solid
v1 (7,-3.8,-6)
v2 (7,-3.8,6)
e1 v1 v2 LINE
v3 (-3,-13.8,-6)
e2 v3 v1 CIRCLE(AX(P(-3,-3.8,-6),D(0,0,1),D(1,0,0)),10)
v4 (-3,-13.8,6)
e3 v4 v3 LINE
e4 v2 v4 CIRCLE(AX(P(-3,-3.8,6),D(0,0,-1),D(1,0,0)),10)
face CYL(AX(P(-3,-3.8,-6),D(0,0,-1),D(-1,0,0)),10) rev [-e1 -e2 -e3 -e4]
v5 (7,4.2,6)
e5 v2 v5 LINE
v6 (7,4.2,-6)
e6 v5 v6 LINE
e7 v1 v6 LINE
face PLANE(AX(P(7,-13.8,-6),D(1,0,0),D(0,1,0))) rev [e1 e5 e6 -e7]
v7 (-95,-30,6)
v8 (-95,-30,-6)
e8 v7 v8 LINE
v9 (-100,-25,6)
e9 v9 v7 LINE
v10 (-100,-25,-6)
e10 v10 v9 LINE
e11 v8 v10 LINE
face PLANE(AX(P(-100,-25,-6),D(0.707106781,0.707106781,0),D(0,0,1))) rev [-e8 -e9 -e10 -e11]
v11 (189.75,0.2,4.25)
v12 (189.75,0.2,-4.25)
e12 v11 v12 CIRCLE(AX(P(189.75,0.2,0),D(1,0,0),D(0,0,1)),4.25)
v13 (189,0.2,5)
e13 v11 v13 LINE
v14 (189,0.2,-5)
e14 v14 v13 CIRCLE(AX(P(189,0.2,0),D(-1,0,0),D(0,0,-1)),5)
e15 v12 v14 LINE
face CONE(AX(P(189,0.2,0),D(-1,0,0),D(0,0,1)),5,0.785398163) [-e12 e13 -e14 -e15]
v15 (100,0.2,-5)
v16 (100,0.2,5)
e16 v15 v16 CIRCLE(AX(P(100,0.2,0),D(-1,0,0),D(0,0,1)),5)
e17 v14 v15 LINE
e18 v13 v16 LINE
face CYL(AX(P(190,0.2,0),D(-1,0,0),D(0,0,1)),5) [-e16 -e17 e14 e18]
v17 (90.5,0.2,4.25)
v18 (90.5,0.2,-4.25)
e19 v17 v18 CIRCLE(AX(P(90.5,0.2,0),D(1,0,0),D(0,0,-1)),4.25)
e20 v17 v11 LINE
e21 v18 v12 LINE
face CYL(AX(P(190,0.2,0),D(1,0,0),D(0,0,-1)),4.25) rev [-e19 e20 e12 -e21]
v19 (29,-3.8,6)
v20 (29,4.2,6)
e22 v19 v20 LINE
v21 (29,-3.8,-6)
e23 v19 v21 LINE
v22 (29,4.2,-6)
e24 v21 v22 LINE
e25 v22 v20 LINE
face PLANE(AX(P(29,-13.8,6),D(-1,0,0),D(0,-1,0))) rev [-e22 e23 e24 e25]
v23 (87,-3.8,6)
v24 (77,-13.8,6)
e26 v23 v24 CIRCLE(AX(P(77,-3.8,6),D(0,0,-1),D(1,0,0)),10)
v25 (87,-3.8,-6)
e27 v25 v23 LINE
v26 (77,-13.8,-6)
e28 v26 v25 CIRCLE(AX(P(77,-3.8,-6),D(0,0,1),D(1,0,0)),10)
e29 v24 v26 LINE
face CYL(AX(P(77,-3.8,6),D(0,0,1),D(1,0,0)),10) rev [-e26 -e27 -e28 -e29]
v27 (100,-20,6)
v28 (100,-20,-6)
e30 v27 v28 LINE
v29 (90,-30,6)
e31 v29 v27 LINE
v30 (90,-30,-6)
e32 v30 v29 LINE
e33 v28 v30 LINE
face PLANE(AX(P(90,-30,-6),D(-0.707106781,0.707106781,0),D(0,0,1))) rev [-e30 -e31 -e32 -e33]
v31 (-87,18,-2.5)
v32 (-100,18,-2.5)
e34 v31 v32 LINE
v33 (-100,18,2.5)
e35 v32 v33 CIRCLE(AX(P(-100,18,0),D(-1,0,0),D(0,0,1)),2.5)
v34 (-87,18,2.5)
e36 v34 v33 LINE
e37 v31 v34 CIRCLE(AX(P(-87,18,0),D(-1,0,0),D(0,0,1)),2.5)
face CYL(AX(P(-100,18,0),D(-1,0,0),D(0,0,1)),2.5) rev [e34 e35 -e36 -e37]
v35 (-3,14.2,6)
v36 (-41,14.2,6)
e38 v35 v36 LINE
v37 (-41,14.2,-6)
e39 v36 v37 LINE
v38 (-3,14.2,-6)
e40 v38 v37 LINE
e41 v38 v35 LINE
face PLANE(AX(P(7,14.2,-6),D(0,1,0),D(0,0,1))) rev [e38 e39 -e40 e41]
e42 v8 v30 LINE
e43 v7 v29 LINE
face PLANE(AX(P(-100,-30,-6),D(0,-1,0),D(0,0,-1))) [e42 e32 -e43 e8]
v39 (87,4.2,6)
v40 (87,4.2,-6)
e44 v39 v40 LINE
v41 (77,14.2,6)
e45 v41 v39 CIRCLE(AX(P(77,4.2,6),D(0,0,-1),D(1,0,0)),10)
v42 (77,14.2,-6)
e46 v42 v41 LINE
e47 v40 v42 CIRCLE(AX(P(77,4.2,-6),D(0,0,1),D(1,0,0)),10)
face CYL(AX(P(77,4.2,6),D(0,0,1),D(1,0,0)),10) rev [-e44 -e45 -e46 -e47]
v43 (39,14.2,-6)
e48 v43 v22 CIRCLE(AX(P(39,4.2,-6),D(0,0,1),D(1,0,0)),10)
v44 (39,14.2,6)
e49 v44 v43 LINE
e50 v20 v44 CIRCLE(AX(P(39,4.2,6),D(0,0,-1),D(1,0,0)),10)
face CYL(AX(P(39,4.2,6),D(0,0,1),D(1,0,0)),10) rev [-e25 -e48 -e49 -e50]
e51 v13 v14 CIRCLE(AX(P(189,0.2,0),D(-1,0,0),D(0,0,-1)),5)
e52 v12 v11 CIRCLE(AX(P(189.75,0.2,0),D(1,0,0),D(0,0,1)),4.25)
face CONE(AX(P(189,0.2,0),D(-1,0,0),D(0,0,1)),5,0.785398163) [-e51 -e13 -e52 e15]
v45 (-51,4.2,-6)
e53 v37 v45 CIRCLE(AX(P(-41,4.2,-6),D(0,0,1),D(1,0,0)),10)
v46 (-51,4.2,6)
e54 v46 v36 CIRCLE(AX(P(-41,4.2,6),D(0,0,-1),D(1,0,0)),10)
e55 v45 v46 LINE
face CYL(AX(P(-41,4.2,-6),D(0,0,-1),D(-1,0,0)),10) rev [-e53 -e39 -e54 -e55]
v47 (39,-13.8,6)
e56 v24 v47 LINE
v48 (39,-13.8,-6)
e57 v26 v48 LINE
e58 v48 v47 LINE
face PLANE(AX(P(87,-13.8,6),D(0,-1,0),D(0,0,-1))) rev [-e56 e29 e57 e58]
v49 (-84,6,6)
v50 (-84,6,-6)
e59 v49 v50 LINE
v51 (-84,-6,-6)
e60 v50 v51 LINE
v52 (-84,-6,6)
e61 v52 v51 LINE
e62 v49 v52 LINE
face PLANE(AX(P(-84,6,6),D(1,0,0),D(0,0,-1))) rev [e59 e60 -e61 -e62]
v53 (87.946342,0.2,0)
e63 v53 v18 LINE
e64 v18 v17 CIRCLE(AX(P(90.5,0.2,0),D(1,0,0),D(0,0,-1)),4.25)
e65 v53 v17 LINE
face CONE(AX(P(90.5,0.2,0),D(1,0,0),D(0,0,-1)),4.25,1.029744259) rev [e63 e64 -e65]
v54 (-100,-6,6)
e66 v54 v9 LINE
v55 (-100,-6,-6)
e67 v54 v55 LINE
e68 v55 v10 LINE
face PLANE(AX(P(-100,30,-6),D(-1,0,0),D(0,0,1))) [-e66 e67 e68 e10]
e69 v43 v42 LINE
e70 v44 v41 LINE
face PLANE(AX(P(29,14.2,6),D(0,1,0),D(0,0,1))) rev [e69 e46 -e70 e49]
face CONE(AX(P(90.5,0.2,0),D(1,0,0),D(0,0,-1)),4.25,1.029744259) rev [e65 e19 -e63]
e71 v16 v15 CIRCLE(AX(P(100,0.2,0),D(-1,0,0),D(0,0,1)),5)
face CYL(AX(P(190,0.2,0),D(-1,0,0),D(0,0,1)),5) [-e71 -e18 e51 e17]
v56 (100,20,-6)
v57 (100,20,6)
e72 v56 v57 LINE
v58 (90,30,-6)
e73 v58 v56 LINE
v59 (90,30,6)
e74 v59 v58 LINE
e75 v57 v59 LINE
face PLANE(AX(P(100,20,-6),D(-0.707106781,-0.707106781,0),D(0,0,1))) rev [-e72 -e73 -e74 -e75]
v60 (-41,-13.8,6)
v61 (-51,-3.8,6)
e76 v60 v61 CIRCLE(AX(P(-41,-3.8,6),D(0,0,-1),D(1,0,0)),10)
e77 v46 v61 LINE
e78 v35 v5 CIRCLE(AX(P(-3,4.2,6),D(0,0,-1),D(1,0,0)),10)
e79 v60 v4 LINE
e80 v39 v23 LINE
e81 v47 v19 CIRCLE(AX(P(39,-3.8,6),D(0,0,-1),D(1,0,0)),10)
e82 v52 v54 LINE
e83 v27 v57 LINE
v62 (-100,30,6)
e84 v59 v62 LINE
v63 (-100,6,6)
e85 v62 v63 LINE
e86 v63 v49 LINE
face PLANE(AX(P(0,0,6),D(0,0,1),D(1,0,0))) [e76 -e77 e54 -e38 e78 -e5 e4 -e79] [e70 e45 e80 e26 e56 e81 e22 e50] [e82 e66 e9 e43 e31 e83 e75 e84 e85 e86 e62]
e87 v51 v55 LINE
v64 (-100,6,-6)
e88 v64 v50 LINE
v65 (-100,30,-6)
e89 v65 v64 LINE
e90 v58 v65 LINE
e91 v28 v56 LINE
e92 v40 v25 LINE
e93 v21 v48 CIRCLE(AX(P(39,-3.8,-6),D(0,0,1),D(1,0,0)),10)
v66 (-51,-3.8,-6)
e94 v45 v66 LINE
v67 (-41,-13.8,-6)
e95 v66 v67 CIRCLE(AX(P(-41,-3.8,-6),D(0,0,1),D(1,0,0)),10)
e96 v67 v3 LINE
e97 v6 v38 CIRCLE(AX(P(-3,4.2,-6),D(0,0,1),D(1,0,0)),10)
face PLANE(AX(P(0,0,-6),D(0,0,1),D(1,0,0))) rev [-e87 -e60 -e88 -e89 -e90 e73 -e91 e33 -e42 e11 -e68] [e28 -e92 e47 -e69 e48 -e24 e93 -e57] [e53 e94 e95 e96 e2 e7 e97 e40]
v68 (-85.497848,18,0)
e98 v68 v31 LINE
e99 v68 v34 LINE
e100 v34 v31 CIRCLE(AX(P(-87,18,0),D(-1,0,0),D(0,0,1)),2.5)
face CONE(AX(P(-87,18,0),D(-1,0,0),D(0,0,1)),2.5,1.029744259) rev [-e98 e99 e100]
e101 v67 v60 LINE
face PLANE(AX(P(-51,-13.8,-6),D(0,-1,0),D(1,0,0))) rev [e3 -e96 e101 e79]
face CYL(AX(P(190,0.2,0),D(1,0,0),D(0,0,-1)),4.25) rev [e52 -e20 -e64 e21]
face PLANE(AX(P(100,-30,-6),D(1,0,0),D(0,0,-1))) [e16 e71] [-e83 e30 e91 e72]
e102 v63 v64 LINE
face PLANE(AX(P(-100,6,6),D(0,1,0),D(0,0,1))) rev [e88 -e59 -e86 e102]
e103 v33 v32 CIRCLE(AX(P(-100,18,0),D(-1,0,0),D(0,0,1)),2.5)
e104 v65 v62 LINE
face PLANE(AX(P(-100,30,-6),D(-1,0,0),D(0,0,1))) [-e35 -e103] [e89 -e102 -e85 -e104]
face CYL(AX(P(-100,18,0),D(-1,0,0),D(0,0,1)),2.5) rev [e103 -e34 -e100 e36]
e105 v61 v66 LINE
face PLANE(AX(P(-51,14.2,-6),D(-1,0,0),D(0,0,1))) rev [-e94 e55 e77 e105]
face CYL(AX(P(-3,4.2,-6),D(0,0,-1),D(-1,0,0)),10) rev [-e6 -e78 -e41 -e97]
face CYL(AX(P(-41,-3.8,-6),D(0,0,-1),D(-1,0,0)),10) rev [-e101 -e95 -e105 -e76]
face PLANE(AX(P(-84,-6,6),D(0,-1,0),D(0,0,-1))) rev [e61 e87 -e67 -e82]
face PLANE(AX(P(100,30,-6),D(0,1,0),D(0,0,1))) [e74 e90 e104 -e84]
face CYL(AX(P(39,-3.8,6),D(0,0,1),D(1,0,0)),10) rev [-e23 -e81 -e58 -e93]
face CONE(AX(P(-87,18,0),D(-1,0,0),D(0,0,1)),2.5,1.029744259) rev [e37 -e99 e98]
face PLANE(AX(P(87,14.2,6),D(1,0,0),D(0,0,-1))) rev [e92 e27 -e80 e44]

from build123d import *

# Parameters (mm, degrees)
SKETCH1_W              = 200
SKETCH1_H              = 60
BOSS_EXTRUDE1_DEPTH    = 12
SKETCH2_W              = 16
SKETCH2_H              = 12
CUT_EXTRUDE1_DEPTH     = 106.090437243
SKETCH3_W              = 58
SKETCH3_H              = 28
CUT_EXTRUDE2_DEPTH     = 106.090437243
SKETCH4_W              = 58
SKETCH4_H              = 28
CUT_EXTRUDE3_DEPTH     = 106.090437243
SKETCH5_W              = 90
SKETCH5_H              = 5
M6_TAPPED_HOLE1_D      = 5
M6_TAPPED_HOLE1_DEPTH  = 13
M6_TAPPED_HOLE1_TIP    = 1.502151548
CHAMFER1_SIZE          = 1
CHAMFER2_SIZE          = 10
CHAMFER3_SIZE          = 5
FILLET1_R              = 10
M10_TAPPED_HOLE1_D     = 8.5
M10_TAPPED_HOLE1_DEPTH = 99.5
M10_TAPPED_HOLE1_TIP   = 2.553657631


with BuildPart() as part:
    # Sketch1 → Boss-Extrude1 (new body)
    with BuildSketch(Plane.XY.offset(6)):
        Rectangle(SKETCH1_W, SKETCH1_H)
    extrude(amount=-BOSS_EXTRUDE1_DEPTH)

    # Sketch2 → Cut-Extrude1 (cut, through all)
    with BuildSketch(Plane(origin=(0, 0, -6), x_dir=(-1, 0, 0), z_dir=(0, 0, -1))):
        with Locations((92, 0)):
            Rectangle(SKETCH2_W, SKETCH2_H)
    extrude(amount=-CUT_EXTRUDE1_DEPTH, mode=Mode.SUBTRACT)

    # Sketch3 → Cut-Extrude2 (cut, through all)
    with BuildSketch(Plane.XY.offset(6)):
        with Locations((-22, 0.2)):
            Rectangle(SKETCH3_W, SKETCH3_H)
    extrude(amount=-CUT_EXTRUDE2_DEPTH, mode=Mode.SUBTRACT)

    # Sketch4 → Cut-Extrude3 (cut, through all)
    with BuildSketch(Plane(origin=(0, 0, -6), x_dir=(-1, 0, 0), z_dir=(0, 0, -1))):
        with Locations((-58, 0.2)):
            Rectangle(SKETCH4_W, SKETCH4_H)
    extrude(amount=-CUT_EXTRUDE3_DEPTH, mode=Mode.SUBTRACT)

    # Sketch5 → Revolve1 (revolve)
    with BuildSketch(Plane(origin=(0, 0, 0), x_dir=(-1, 0, 0), z_dir=(0, 0, -1)), mode=Mode.PRIVATE) as revolve1_sk:
        with Locations((-145, 2.7)):
            Rectangle(SKETCH5_W, SKETCH5_H)
    revolve(revolve1_sk.sketch.rotate(Axis((190, 0.2, 0), (-1, 0, 0)), 270), axis=Axis((190, 0.2, 0), (-1, 0, 0)))

    # M6 Tapped Hole1
    with Locations(Plane.ZY.offset(100)):
        with Locations((0, 18)):
            Hole(M6_TAPPED_HOLE1_D / 2, depth=M6_TAPPED_HOLE1_DEPTH)
            with Locations((0, 0, -(M6_TAPPED_HOLE1_DEPTH + M6_TAPPED_HOLE1_TIP / 2))):  # 118° drill point
                Cone(0, M6_TAPPED_HOLE1_D / 2, M6_TAPPED_HOLE1_TIP, mode=Mode.SUBTRACT)

    # Chamfer1
    chamfer1_edges = [part.edges().sort_by_distance(p)[0] for p in [
        (190, 0.2, -5),
    ]]
    chamfer(chamfer1_edges, length=CHAMFER1_SIZE)

    # Chamfer2
    chamfer2_edges = [part.edges().sort_by_distance(p)[0] for p in [
        (100, 30, 0),
        (100, -30, 0),
    ]]
    chamfer(chamfer2_edges, length=CHAMFER2_SIZE)

    # Chamfer3
    chamfer3_edges = [part.edges().sort_by_distance(p)[0] for p in [
        (-100, -30, 0),
    ]]
    chamfer(chamfer3_edges, length=CHAMFER3_SIZE)

    # Fillet1
    fillet1_edges = [part.edges().sort_by_distance(p)[0] for p in [
        (-51, -13.8, 0),
        (-51, 14.2, 0),
        (7, 14.2, 0),
        (7, -13.8, 0),
        (29, 14.2, 0),
        (29, -13.8, 0),
        (87, -13.8, 0),
        (87, 14.2, 0),
    ]]
    fillet(fillet1_edges, radius=FILLET1_R)

    # M10 Tapped Hole1
    with Locations(Plane(origin=(190, 0, 0), x_dir=(0, 0, -1), z_dir=(1, 0, 0))):
        with Locations((0, 0.2)):
            Hole(M10_TAPPED_HOLE1_D / 2, depth=M10_TAPPED_HOLE1_DEPTH)
            with Locations((0, 0, -(M10_TAPPED_HOLE1_DEPTH + M10_TAPPED_HOLE1_TIP / 2))):  # 118° drill point
                Cone(0, M10_TAPPED_HOLE1_D / 2, M10_TAPPED_HOLE1_TIP, mode=Mode.SUBTRACT)


solid = part.part
